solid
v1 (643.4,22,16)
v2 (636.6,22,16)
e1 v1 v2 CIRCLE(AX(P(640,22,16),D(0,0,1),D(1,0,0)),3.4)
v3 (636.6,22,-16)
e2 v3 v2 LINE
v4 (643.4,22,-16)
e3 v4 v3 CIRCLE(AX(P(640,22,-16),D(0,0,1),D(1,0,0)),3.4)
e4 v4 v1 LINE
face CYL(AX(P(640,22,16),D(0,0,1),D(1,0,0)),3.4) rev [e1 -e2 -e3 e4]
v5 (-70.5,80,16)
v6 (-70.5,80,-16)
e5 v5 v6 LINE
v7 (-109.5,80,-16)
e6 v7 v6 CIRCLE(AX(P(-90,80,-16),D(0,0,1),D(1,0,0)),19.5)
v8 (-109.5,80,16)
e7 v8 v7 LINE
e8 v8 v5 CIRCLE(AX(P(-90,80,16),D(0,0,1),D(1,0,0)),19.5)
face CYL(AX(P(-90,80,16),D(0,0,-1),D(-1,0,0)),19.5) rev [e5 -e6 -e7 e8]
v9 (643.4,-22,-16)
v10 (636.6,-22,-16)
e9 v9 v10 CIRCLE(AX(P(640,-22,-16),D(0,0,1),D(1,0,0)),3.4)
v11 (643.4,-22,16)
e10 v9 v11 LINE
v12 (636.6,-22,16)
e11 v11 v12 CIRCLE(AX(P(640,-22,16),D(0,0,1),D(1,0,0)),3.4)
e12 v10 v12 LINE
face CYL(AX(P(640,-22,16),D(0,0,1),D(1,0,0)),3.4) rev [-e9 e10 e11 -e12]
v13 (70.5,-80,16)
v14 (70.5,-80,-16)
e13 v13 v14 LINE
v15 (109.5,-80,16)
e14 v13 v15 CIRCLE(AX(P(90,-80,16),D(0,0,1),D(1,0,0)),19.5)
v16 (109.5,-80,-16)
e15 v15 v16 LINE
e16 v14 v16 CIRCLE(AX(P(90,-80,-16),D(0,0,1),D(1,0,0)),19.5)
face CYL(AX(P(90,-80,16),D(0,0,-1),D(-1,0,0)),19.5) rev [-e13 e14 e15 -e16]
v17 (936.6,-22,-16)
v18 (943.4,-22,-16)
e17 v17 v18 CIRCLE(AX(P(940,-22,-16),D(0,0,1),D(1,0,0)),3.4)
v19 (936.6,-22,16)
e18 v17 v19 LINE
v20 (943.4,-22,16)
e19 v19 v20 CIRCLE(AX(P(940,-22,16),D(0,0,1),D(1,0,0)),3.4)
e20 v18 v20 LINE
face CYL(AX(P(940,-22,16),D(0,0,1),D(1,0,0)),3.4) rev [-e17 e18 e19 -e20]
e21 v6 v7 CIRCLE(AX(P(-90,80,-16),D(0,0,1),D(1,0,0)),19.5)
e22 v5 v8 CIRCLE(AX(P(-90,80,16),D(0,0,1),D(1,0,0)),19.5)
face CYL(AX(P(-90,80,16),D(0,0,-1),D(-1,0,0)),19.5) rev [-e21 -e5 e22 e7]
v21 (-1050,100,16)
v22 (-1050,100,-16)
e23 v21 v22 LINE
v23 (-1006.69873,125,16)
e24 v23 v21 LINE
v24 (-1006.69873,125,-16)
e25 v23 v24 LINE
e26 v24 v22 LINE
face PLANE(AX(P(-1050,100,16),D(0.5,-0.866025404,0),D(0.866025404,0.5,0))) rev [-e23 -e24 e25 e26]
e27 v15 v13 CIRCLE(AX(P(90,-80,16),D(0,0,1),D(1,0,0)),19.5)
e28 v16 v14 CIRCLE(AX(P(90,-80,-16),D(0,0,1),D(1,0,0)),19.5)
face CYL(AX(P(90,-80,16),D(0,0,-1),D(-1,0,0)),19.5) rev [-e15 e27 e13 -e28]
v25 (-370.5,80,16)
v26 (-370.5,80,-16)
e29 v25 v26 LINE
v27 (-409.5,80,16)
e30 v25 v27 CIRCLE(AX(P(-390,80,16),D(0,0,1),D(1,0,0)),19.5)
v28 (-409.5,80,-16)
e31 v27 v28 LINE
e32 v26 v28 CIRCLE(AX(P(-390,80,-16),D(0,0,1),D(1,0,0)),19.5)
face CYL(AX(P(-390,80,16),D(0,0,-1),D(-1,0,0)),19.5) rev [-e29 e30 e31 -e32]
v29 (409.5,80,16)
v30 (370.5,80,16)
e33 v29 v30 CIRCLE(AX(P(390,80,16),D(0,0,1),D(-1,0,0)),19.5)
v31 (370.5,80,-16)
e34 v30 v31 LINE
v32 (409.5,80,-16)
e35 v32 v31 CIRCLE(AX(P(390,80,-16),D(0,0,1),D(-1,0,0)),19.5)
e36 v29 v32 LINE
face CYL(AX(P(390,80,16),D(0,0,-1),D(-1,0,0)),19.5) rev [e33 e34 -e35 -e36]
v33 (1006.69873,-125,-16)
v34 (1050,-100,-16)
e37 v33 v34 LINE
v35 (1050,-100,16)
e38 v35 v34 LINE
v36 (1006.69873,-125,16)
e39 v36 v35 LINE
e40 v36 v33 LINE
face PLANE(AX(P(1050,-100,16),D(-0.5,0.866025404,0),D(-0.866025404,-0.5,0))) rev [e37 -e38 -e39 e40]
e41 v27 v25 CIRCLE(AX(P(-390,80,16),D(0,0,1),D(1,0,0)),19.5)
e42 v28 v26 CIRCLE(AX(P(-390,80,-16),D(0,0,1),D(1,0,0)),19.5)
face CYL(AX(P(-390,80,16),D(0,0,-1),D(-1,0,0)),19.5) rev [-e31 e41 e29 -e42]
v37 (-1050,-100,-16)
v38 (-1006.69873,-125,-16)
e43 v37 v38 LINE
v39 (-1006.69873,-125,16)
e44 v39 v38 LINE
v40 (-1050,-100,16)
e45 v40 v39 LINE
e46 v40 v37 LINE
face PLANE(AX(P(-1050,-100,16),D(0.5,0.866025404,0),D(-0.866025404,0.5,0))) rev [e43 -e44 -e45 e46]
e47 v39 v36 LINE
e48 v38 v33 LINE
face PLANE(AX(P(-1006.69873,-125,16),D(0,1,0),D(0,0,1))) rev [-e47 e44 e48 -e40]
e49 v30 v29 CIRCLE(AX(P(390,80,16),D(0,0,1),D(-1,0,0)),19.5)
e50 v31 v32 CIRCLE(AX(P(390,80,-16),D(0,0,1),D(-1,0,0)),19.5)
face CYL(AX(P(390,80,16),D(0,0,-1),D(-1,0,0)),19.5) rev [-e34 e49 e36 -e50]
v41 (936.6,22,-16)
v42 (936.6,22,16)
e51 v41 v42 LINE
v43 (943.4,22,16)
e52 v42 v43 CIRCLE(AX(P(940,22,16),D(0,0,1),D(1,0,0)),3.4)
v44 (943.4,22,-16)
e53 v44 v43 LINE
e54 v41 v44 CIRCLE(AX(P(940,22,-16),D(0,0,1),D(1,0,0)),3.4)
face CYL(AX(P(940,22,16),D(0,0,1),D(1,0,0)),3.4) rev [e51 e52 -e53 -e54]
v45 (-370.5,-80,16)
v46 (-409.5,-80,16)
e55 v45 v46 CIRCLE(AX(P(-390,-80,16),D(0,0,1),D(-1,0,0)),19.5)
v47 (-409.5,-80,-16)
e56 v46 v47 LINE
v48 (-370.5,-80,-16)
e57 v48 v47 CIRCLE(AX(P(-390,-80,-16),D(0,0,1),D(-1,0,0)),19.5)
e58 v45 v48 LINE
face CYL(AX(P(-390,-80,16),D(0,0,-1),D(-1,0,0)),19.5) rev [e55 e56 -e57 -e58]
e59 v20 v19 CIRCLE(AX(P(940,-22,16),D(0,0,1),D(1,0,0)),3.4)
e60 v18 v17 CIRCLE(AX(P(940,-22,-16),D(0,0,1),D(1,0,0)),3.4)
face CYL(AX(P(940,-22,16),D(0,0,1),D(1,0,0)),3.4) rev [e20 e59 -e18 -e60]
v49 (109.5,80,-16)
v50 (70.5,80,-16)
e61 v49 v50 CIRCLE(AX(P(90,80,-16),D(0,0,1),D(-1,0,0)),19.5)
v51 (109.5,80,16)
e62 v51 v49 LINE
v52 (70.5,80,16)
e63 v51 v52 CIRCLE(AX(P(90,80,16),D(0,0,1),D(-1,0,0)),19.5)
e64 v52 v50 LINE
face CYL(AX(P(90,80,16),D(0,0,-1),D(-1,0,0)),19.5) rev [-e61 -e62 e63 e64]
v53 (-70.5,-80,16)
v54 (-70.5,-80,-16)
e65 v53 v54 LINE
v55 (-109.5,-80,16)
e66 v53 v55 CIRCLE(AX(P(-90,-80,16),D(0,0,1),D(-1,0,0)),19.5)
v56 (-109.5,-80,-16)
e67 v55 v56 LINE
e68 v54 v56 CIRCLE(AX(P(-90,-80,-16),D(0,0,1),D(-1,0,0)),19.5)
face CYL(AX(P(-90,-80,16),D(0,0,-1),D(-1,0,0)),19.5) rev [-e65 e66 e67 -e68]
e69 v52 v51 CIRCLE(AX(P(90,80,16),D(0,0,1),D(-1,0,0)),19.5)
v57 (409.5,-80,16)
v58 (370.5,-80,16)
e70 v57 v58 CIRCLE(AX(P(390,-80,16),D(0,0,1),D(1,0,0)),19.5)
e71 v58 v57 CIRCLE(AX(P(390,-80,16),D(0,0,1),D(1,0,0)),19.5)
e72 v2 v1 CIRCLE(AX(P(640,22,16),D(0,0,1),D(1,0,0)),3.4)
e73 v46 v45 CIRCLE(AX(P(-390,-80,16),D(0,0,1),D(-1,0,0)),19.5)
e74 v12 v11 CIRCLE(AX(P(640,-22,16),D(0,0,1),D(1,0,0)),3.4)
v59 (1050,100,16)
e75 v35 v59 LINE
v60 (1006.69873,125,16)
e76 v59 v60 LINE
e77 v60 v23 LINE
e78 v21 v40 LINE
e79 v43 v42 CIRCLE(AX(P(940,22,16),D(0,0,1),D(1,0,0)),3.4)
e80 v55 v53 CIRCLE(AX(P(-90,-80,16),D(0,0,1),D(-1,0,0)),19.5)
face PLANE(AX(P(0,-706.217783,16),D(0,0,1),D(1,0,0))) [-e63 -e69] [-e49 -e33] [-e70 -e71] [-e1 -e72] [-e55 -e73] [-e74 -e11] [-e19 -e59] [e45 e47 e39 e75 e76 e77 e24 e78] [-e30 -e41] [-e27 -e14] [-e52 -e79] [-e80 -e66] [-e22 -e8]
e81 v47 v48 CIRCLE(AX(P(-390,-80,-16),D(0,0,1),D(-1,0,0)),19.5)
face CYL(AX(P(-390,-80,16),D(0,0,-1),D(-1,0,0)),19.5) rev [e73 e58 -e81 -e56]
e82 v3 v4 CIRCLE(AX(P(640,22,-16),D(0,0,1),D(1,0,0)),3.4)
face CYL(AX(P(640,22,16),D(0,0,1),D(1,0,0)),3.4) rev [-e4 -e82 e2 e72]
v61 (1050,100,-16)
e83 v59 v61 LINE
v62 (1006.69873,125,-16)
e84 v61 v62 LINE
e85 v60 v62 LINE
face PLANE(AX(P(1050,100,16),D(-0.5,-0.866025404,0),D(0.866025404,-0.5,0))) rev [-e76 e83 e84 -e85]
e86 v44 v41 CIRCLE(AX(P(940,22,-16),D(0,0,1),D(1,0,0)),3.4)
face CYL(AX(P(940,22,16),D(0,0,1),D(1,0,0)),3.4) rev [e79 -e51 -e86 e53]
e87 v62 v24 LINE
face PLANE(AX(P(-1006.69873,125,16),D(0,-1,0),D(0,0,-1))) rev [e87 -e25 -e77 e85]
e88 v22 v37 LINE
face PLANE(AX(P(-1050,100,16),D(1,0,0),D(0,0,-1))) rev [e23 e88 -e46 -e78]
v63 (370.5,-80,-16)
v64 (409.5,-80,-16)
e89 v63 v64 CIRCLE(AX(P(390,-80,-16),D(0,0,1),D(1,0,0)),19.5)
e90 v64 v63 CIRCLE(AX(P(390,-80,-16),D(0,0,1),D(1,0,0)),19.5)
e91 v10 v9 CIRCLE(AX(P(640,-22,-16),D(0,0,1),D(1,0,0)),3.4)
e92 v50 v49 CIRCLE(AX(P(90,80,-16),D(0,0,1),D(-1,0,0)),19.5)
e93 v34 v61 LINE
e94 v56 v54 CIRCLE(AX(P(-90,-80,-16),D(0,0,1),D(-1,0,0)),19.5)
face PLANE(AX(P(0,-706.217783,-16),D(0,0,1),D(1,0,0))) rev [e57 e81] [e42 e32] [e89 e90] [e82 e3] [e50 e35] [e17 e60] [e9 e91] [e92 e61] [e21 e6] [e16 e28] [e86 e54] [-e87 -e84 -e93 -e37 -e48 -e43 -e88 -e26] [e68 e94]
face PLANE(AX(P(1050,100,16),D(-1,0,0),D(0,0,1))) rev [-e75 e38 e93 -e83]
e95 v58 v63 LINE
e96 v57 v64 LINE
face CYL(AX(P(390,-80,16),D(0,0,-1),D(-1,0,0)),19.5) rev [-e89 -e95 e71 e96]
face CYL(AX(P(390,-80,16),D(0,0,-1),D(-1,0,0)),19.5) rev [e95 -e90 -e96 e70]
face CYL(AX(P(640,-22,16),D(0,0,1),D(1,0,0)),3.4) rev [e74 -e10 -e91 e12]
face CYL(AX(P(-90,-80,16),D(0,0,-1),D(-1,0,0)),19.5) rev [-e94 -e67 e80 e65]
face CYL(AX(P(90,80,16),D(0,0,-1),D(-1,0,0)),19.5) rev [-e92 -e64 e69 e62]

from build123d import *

# Parameters (mm, degrees)
SKETCH1_R            = 19.5
BOSS_EXTRUDE1_DEPTH  = 16
M8_TAPPED_HOLE1_D    = 6.8
LPATTERN1_COUNT      = 2
LPATTERN1_PITCH      = 300
LPATTERN1_COUNT_DIR2 = 2
LPATTERN1_PITCH_DIR2 = 44


with BuildPart() as part:
    # Sketch1 → Boss-Extrude1 (new, symmetric)
    with BuildSketch(Plane.XY):
        Polygon((1050, 100), (1006.698729811, 125), (-1006.698729811, 125), (-1050, 100), (-1050, -100), (-1006.698729811, -125), (1006.698729811, -125), (1050, -100), align=None)
        with Locations((-390, 80)):
            Circle(SKETCH1_R, mode=Mode.SUBTRACT)
        with Locations((-90, 80)):
            Circle(SKETCH1_R, mode=Mode.SUBTRACT)
        with Locations(Location((-90, -80, 0), (0, 0, 180))):
            Circle(SKETCH1_R, mode=Mode.SUBTRACT)
        with Locations(Location((-390, -80, 0), (0, 0, 180))):
            Circle(SKETCH1_R, mode=Mode.SUBTRACT)
        with Locations((390, -80)):
            Circle(SKETCH1_R, mode=Mode.SUBTRACT)
        with Locations((90, -80)):
            Circle(SKETCH1_R, mode=Mode.SUBTRACT)
        with Locations(Location((90, 80, 0), (0, 0, 180))):
            Circle(SKETCH1_R, mode=Mode.SUBTRACT)
        with Locations(Location((390, 80, 0), (0, 0, 180))):
            Circle(SKETCH1_R, mode=Mode.SUBTRACT)
    extrude(amount=BOSS_EXTRUDE1_DEPTH, both=True)

    # M8 Tapped Hole1 (through all)
    with Locations(Plane.XY.offset(16)):
        with Locations((640, 22)):
            m8_tapped_hole1 = Hole(M8_TAPPED_HOLE1_D / 2)

    # LPattern1: M8 Tapped Hole1 2 × 2
    with Locations(*[(i * LPATTERN1_PITCH, -j * LPATTERN1_PITCH_DIR2, 0) for i in range(LPATTERN1_COUNT) for j in range(LPATTERN1_COUNT_DIR2) if (i, j) != (0, 0)]):
        add(m8_tapped_hole1, mode=Mode.SUBTRACT)


solid = part.part
